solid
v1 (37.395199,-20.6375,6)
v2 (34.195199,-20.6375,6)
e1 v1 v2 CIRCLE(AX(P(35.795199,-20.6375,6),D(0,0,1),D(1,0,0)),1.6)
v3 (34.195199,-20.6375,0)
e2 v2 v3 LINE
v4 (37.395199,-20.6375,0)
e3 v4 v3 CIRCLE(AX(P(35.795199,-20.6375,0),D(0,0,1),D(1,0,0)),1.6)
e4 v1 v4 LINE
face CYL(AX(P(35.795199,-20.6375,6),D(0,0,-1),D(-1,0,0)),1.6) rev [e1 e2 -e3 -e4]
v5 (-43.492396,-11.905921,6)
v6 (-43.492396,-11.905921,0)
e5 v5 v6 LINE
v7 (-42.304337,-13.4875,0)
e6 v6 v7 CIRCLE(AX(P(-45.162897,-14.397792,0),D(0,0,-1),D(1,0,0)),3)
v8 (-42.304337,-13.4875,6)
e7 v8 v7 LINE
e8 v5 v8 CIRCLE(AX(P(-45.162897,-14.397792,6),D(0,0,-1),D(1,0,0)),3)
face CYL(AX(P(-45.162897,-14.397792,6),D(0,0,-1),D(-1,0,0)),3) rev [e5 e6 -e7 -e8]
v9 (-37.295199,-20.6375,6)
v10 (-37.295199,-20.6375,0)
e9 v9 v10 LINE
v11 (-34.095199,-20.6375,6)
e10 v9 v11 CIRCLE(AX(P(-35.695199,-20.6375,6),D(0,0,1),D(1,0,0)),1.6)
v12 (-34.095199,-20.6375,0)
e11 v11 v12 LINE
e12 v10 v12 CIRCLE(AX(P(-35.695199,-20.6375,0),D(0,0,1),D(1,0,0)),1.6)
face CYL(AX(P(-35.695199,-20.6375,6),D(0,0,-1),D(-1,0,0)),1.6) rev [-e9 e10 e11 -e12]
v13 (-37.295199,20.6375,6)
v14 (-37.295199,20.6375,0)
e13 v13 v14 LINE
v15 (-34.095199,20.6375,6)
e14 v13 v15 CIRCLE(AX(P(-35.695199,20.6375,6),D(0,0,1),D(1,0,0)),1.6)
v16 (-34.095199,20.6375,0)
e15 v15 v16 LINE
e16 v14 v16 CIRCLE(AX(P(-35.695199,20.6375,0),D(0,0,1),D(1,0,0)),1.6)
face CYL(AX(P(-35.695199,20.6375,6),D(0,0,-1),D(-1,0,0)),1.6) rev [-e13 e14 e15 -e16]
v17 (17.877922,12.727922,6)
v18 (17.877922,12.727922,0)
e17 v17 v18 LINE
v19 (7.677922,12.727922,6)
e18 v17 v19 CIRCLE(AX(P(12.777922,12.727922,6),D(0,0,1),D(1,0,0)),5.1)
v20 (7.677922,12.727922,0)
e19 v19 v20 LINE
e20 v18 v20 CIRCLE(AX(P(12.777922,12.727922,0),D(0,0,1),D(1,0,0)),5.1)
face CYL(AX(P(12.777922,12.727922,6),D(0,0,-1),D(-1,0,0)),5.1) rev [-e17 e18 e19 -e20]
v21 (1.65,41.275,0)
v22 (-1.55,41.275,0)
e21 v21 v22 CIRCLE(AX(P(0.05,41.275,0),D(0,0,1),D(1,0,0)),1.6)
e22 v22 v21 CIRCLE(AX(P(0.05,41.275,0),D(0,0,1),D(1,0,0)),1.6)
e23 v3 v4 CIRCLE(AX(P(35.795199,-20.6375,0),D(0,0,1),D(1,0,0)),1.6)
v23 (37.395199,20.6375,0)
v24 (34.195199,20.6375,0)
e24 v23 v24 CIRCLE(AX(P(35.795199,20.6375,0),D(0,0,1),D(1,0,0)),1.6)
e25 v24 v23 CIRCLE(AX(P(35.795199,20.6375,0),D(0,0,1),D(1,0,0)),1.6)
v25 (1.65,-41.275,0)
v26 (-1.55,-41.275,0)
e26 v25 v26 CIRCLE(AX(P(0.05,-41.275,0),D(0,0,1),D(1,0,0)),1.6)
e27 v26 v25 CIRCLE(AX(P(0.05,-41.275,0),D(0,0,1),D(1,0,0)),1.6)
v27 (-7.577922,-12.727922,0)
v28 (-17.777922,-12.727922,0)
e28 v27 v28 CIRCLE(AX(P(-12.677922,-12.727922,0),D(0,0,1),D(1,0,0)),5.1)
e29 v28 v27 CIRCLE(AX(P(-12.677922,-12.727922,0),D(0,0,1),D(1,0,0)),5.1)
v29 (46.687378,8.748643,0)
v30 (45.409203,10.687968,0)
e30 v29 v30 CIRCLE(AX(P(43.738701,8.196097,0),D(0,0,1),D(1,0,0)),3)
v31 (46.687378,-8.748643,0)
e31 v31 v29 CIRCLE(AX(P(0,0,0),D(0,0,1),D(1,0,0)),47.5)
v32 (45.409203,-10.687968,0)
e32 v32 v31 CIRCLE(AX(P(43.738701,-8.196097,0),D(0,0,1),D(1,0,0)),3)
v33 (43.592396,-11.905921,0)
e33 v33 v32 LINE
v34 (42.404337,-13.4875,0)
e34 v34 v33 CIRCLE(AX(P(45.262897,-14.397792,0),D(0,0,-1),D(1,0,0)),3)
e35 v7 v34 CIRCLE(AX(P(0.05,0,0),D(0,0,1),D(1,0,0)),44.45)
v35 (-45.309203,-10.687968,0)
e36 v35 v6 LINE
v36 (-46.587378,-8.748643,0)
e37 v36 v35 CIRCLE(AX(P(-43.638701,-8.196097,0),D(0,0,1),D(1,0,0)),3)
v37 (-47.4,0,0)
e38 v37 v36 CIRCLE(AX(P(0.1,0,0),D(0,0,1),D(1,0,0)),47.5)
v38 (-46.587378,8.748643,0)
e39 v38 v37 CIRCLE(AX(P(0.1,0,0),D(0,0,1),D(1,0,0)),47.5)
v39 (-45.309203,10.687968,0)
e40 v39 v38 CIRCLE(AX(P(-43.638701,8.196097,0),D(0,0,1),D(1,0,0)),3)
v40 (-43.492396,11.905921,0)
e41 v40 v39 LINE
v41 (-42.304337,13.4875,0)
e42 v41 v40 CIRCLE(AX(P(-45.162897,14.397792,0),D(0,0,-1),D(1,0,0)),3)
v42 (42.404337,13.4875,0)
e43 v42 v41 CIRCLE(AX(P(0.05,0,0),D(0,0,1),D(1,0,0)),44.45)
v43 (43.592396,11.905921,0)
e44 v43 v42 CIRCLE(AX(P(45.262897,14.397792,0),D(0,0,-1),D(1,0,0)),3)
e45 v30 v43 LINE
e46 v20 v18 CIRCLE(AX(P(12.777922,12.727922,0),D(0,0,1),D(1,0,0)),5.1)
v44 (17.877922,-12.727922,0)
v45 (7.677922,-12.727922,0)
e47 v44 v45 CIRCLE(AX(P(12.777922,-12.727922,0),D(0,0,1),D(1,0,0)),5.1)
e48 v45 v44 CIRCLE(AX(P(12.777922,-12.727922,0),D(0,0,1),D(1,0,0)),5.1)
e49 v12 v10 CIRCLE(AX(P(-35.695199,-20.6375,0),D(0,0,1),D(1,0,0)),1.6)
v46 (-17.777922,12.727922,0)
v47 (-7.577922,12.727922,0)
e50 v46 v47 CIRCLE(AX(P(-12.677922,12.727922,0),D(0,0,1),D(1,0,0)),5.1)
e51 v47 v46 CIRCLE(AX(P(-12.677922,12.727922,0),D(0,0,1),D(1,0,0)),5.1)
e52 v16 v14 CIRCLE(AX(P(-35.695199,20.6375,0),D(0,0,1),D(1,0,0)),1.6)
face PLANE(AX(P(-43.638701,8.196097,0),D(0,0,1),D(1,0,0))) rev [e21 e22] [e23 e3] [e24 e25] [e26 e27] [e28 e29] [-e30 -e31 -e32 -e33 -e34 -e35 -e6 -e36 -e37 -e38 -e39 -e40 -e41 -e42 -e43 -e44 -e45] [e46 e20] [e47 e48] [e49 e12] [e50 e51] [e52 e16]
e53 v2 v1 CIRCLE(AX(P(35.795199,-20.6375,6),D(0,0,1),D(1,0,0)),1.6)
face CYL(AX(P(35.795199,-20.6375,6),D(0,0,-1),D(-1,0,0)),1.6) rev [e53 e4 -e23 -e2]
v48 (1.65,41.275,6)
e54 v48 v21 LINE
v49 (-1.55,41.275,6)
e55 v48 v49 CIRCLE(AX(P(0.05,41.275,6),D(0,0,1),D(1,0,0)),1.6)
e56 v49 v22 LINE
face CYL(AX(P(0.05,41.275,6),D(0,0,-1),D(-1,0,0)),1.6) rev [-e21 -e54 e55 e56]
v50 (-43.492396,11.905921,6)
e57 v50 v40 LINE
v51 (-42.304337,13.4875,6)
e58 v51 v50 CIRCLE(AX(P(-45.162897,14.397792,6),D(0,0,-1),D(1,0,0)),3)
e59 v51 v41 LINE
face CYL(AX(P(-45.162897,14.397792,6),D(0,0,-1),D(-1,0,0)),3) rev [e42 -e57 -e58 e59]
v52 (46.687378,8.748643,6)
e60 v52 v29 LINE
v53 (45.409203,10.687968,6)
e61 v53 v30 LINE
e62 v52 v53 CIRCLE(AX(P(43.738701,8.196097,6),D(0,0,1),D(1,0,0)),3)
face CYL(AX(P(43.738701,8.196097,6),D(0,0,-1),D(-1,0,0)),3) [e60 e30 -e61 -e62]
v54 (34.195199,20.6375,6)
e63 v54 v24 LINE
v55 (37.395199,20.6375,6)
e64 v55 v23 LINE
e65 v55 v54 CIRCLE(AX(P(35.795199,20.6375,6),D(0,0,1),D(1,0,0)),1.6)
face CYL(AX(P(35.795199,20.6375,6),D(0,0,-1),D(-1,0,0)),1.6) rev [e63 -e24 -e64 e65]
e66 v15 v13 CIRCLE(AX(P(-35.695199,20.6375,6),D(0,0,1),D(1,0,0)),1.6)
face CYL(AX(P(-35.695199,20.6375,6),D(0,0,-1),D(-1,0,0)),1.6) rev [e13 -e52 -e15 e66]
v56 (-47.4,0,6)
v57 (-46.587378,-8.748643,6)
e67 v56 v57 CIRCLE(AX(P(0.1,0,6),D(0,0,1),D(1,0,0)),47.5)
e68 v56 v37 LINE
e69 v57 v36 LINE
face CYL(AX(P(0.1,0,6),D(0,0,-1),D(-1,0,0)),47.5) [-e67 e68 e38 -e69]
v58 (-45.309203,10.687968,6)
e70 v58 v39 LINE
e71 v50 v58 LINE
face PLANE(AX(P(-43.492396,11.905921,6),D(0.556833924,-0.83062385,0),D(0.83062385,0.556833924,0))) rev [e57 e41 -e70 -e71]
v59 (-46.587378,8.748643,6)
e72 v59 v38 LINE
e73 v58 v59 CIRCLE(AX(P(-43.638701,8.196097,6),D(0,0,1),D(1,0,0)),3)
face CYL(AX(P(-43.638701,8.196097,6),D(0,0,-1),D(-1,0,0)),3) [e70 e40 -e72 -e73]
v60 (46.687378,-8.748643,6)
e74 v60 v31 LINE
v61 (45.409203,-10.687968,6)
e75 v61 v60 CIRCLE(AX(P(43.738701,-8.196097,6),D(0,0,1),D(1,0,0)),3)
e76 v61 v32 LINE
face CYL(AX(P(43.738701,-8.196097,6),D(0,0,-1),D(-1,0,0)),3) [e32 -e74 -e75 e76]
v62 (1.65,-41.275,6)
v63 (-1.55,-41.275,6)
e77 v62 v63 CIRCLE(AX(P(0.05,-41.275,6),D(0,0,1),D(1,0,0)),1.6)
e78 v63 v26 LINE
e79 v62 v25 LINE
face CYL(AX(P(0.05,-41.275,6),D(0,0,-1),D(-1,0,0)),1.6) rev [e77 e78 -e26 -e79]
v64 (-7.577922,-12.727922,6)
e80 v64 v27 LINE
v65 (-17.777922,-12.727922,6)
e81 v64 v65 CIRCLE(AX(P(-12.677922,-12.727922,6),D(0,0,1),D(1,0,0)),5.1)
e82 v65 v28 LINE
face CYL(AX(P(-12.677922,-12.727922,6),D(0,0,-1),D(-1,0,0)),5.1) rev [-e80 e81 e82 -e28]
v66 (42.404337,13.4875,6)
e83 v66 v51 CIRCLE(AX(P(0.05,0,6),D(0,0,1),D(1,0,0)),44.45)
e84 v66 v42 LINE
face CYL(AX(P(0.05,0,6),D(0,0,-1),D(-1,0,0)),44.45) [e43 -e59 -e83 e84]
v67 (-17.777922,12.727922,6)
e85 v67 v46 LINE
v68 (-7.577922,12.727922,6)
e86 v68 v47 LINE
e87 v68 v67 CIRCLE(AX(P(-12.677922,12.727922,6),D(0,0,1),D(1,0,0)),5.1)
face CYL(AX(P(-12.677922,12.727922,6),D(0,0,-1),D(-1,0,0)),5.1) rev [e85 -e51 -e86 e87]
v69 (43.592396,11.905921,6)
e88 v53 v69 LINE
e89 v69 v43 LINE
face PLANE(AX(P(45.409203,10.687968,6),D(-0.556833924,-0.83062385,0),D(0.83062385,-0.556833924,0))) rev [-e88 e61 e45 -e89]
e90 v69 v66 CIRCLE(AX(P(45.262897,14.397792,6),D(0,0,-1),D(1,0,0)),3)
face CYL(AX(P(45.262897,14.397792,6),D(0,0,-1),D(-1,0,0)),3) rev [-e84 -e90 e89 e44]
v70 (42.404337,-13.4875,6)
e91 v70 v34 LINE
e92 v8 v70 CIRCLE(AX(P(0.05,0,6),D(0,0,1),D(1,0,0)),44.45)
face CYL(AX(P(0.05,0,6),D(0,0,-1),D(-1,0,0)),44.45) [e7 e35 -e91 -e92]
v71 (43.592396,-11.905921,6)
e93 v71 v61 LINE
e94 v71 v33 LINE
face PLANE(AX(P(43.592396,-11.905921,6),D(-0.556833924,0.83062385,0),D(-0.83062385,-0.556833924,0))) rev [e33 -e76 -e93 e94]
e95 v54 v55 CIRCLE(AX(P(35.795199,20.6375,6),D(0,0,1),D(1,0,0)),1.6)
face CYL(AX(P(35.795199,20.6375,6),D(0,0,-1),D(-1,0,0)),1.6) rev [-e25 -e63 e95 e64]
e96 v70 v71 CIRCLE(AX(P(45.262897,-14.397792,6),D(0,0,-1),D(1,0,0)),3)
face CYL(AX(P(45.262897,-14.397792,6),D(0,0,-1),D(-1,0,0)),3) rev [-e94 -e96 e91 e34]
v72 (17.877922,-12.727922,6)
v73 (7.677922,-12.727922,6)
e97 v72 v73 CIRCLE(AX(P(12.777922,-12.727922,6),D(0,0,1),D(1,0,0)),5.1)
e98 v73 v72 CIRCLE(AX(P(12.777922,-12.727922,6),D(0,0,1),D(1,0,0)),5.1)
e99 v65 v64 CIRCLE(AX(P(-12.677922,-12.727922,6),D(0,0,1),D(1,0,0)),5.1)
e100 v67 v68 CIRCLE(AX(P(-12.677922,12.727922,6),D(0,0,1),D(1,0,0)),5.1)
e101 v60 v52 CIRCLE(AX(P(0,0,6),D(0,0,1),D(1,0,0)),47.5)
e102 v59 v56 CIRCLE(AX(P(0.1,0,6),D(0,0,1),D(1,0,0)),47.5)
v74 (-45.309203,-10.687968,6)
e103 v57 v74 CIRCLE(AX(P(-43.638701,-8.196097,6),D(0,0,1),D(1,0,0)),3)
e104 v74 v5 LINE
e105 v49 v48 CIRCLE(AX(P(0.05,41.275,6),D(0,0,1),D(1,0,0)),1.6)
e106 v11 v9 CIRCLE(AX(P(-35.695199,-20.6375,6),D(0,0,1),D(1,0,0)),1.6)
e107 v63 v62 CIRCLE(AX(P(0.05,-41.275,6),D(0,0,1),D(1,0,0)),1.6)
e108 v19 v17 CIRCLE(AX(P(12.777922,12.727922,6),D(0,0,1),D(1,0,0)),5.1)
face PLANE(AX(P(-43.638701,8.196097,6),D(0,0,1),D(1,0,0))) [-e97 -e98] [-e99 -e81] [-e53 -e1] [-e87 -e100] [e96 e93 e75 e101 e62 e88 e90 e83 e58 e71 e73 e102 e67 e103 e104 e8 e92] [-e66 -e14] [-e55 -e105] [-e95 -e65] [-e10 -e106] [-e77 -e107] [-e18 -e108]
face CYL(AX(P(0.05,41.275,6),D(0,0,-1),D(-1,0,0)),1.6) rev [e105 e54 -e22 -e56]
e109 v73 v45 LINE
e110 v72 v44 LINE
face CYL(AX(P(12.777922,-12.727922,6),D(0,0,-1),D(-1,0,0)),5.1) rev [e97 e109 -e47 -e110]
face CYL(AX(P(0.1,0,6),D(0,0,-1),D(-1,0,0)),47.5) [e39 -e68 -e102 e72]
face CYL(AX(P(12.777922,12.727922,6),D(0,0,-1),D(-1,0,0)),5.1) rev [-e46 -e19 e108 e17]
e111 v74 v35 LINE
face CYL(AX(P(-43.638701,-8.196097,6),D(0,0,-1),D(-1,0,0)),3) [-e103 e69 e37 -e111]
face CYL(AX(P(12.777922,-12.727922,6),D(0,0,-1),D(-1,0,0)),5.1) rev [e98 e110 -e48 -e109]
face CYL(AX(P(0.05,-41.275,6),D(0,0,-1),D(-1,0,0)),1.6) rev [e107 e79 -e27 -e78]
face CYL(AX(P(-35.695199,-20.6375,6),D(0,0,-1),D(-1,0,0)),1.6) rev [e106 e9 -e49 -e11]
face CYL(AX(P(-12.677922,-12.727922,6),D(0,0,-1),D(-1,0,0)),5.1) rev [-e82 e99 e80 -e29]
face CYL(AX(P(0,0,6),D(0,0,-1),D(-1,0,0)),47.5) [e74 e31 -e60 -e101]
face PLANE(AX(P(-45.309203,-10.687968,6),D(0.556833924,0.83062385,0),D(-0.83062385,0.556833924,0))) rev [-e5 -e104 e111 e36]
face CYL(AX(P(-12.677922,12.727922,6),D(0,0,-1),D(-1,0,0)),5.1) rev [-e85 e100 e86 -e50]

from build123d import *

# Parameters (mm, degrees)
SKETCH1_R           = 1.6
SKETCH1_R_2         = 5.1
BOSS_EXTRUDE1_DEPTH = 6


with BuildPart() as part:
    # Sketch1 → Boss-Extrude1 (new body)
    with BuildSketch(Plane.XY):
        with BuildLine():
            Line((-45.309203126, -10.68796842), (-43.492395524, -11.905920573))
            ThreePointArc((-43.492395524, -11.905920573), (-42.764262434, -12.595973377), (-42.304336877, -13.487499682))
            ThreePointArc((-42.304336877, -13.487499682), (0.05, -44.45), (42.404336877, -13.487499682))
            ThreePointArc((42.404336877, -13.487499682), (42.864262434, -12.595973377), (43.592395524, -11.905920573))
            Line((43.592395524, -11.905920573), (45.409203126, -10.68796842))
            ThreePointArc((45.409203126, -10.68796842), (46.243586183, -9.847021456), (46.68737785, -8.748642725))
            ThreePointArc((46.68737785, -8.748642725), (47.5, 0), (46.68737785, 8.748642725))
            ThreePointArc((46.68737785, 8.748642725), (46.243586183, 9.847021456), (45.409203126, 10.68796842))
            Line((45.409203126, 10.68796842), (43.592395524, 11.905920573))
            ThreePointArc((43.592395524, 11.905920573), (42.864262434, 12.595973377), (42.404336877, 13.487499682))
            ThreePointArc((42.404336877, 13.487499682), (0.05, 44.45), (-42.304336877, 13.487499682))
            ThreePointArc((-42.304336877, 13.487499682), (-42.764262434, 12.595973377), (-43.492395524, 11.905920573))
            Line((-43.492395524, 11.905920573), (-45.309203126, 10.68796842))
            ThreePointArc((-45.309203126, 10.68796842), (-46.143586183, 9.847021456), (-46.58737785, 8.748642725))
            ThreePointArc((-46.58737785, 8.748642725), (-47.4, 0), (-46.58737785, -8.748642725))
            ThreePointArc((-46.58737785, -8.748642725), (-46.143586183, -9.847021456), (-45.309203126, -10.68796842))
        make_face()
        with Locations((-35.695198541, 20.6375)):
            Circle(SKETCH1_R, mode=Mode.SUBTRACT)
        with Locations((-35.695198541, -20.6375)):
            Circle(SKETCH1_R, mode=Mode.SUBTRACT)
        with Locations((35.795198541, -20.6375)):
            Circle(SKETCH1_R, mode=Mode.SUBTRACT)
        with Locations((35.795198541, 20.6375)):
            Circle(SKETCH1_R, mode=Mode.SUBTRACT)
        with Locations((12.777922061, 12.727922061)):
            Circle(SKETCH1_R_2, mode=Mode.SUBTRACT)
        with Locations((12.777922061, -12.727922061)):
            Circle(SKETCH1_R_2, mode=Mode.SUBTRACT)
        with Locations((-12.677922061, -12.727922061)):
            Circle(SKETCH1_R_2, mode=Mode.SUBTRACT)
        with Locations((-12.677922061, 12.727922061)):
            Circle(SKETCH1_R_2, mode=Mode.SUBTRACT)
        with Locations((0.05, -41.275)):
            Circle(SKETCH1_R, mode=Mode.SUBTRACT)
        with Locations((0.05, 41.275)):
            Circle(SKETCH1_R, mode=Mode.SUBTRACT)
    extrude(amount=BOSS_EXTRUDE1_DEPTH)


solid = part.part
